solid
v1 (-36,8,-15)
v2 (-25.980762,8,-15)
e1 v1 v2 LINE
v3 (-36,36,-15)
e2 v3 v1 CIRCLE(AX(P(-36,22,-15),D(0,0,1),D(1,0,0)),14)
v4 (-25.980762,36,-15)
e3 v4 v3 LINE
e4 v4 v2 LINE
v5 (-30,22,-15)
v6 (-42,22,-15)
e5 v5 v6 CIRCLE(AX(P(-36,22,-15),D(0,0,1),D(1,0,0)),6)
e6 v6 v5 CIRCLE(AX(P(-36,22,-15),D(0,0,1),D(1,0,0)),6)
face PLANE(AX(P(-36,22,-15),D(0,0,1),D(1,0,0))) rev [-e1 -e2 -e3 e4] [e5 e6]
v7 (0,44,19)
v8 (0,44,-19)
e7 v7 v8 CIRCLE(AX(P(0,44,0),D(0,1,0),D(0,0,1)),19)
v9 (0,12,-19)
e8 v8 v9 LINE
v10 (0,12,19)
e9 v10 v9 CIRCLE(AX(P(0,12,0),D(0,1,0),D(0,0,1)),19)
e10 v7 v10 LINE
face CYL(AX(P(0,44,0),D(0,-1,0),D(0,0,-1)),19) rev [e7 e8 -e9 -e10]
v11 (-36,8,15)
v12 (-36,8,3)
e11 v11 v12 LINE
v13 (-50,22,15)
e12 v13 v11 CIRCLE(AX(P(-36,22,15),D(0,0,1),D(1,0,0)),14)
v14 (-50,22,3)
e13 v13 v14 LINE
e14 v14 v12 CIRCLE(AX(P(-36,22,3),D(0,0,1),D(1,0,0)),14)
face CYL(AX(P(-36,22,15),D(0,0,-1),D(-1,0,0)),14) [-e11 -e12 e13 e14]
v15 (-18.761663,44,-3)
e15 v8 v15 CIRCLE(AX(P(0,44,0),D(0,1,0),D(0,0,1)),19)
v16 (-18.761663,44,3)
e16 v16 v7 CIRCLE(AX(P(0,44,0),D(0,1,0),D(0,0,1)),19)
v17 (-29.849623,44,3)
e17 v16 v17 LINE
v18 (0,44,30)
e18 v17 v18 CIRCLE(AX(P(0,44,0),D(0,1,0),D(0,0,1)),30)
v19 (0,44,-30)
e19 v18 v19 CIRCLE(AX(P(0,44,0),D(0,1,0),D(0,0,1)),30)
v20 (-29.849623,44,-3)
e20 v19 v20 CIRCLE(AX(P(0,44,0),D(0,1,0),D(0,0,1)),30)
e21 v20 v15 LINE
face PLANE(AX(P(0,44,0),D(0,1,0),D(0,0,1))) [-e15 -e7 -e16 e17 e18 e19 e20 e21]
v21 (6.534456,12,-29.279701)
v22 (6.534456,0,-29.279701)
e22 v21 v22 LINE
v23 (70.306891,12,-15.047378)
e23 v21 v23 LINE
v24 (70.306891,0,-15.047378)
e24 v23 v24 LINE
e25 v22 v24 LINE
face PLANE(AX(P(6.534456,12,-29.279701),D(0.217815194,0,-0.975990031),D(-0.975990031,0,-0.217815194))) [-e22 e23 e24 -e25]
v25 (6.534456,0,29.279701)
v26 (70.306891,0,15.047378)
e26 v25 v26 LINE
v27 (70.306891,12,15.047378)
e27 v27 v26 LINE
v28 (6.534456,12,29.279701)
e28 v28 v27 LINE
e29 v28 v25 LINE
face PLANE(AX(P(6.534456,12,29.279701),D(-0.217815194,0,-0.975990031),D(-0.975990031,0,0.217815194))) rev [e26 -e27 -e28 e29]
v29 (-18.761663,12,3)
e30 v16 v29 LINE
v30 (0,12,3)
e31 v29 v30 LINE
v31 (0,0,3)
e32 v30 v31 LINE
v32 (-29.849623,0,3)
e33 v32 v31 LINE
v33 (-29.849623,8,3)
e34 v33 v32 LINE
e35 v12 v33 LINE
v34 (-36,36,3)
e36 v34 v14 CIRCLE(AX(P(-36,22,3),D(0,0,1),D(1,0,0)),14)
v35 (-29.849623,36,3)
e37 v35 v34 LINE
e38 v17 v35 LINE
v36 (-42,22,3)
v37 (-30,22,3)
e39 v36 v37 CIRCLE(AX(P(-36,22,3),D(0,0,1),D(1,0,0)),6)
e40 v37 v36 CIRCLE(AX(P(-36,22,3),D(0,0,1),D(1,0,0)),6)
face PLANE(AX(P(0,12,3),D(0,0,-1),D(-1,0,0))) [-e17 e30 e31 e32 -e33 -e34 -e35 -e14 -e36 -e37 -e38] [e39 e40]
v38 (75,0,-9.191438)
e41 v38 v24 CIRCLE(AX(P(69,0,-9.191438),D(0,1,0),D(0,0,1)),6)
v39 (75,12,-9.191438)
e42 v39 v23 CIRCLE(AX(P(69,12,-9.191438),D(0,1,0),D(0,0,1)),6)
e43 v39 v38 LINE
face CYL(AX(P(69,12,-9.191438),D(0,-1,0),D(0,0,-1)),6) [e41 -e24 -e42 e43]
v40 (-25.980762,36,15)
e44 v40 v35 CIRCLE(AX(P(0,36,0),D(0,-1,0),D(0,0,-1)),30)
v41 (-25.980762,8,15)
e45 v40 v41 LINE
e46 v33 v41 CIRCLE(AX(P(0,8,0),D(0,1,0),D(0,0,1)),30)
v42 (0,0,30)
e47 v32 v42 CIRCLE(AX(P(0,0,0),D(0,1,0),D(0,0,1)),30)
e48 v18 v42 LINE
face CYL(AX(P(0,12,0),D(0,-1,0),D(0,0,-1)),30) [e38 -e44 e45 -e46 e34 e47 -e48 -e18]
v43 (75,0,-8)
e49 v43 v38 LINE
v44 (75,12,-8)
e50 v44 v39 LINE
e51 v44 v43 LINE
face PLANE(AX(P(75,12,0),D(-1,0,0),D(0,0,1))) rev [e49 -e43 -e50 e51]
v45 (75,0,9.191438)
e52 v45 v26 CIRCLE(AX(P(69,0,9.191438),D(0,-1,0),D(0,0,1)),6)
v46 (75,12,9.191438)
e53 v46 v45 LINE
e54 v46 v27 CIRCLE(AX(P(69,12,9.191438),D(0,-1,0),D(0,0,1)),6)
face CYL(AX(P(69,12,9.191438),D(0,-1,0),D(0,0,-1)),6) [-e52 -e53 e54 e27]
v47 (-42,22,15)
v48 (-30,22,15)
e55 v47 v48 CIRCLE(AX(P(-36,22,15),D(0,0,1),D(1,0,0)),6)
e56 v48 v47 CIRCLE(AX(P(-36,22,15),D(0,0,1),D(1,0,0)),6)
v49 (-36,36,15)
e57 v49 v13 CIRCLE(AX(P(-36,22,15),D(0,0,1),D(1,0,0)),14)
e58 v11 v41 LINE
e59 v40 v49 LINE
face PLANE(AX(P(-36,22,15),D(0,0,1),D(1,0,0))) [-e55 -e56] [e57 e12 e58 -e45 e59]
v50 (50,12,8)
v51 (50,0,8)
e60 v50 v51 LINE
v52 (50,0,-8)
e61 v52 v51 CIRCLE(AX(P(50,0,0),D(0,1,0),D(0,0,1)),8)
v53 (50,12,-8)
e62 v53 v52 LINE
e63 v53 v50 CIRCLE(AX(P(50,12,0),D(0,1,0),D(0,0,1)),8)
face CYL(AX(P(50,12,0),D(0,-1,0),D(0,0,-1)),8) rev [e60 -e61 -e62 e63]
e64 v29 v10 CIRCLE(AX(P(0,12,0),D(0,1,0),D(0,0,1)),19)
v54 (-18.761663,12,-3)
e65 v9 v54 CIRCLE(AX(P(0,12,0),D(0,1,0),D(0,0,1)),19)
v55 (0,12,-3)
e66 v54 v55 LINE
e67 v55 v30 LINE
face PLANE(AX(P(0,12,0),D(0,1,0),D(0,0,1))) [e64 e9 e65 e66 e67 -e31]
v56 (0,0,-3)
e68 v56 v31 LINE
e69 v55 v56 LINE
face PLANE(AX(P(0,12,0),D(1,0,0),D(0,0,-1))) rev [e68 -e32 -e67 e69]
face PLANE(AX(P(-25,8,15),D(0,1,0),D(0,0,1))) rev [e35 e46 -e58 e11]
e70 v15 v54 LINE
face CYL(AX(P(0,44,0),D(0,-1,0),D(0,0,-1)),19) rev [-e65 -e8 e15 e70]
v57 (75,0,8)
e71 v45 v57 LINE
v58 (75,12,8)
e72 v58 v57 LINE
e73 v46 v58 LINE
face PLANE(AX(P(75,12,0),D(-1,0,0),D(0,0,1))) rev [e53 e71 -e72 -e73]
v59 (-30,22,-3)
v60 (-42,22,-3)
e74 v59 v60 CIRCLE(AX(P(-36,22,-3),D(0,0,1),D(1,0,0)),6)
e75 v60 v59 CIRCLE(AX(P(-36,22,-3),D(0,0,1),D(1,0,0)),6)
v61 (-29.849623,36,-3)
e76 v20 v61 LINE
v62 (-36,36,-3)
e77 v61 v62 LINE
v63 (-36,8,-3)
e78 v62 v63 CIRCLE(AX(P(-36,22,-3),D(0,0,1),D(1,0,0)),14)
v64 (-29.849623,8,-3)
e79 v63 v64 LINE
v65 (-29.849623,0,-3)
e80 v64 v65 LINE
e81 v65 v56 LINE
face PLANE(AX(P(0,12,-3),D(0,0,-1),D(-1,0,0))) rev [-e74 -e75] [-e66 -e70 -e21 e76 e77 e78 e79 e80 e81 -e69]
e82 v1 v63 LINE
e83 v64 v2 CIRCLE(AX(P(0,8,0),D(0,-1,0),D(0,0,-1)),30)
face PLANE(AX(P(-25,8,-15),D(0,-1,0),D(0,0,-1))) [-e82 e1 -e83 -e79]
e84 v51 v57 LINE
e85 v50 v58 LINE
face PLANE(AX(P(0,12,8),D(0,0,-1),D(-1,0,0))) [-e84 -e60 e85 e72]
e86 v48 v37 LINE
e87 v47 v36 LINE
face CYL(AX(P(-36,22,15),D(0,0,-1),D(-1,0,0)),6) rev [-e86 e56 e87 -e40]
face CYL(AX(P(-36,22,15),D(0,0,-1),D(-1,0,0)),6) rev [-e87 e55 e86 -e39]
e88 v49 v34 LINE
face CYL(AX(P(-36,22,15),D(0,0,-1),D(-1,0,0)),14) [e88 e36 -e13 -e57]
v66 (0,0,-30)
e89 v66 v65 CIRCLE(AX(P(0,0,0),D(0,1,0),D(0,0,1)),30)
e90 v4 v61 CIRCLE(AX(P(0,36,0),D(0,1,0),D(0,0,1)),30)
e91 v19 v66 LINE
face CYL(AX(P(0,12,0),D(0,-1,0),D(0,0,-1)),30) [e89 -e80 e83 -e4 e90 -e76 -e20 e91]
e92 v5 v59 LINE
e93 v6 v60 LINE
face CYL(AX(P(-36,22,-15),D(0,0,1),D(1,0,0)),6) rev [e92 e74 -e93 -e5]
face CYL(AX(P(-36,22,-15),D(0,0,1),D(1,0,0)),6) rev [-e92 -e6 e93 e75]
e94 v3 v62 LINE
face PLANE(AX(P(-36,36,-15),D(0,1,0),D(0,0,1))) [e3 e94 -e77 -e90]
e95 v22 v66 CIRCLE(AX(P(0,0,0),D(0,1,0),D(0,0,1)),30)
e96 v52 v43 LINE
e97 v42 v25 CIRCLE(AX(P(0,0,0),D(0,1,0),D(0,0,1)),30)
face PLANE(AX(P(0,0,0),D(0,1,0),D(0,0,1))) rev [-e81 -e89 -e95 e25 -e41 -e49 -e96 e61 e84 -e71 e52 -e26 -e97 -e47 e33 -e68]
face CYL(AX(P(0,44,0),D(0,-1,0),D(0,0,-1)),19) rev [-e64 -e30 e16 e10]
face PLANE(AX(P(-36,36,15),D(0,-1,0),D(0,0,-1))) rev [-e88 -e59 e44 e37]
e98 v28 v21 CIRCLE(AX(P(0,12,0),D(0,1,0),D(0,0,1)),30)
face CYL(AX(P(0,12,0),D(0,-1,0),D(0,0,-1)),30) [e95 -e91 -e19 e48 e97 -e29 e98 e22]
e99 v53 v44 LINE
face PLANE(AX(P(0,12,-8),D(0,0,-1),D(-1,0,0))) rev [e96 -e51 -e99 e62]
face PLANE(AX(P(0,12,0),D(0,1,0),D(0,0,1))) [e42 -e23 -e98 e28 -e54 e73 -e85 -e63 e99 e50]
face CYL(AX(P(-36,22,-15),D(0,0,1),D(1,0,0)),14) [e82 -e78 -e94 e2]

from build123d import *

# Parameters (mm, degrees)
BASE_FLANGE_DEPTH      = 12
SPLIT_CLAMP_RING_DEPTH = 32
CLAMP_EAR_A_SKETCH_R   = 6
CLAMP_EAR_A_DEPTH      = 12
CLAMP_START            = -12
CLAMP_EAR_B_SKETCH_R   = 6
CLAMP_EAR_B_DEPTH      = 12


with BuildPart() as part:
    # Base Flange Sketch → Base Flange (new body)
    with BuildSketch(Plane(origin=(0, 0, 0), x_dir=(1, 0, 0), z_dir=(0, 1, 0))):
        with BuildLine():
            Line((-29.849623113, 3), (0, 3))
            Line((0, 3), (0, -3))
            Line((0, -3), (-29.849623113, -3))
            ThreePointArc((-29.849623113, -3), (-17.565731604, -24.319643772), (6.534455825, -29.279700939))
            Line((6.534455825, -29.279700939), (70.306891165, -15.047377923))
            ThreePointArc((70.306891165, -15.047377923), (73.681951889, -12.943680599), (75, -9.191437735))
            Line((75, -9.191437735), (75, -8))
            Line((75, -8), (50, -8))
            ThreePointArc((50, -8), (42, 0), (50, 8))
            Line((50, 8), (75, 8))
            Line((75, 8), (75, 9.191437735))
            ThreePointArc((75, 9.191437735), (73.681951889, 12.943680599), (70.306891165, 15.047377923))
            Line((70.306891165, 15.047377923), (6.534455825, 29.279700939))
            ThreePointArc((6.534455825, 29.279700939), (-17.565731604, 24.319643772), (-29.849623113, 3))
        make_face()
    extrude(amount=BASE_FLANGE_DEPTH)

    # Clamp Ring Sketch → Split Clamp Ring (add)
    with BuildSketch(Plane(origin=(0, 12, 0), x_dir=(1, 0, 0), z_dir=(0, 1, 0))):
        with BuildLine():
            ThreePointArc((6.534455825, 29.279700939), (-17.565731604, 24.319643772), (-29.849623113, 3))
            Line((-29.849623113, 3), (-18.761663039, 3))
            ThreePointArc((-18.761663039, 3), (19, 0), (-18.761663039, -3))
            Line((-18.761663039, -3), (-29.849623113, -3))
            ThreePointArc((-29.849623113, -3), (-17.565731604, -24.319643772), (6.534455825, -29.279700939))
            ThreePointArc((6.534455825, -29.279700939), (30, 0), (6.534455825, 29.279700939))
        make_face()
    extrude(amount=SPLIT_CLAMP_RING_DEPTH)

    # Clamp Ear A Sketch → Clamp Ear A (add)
    with BuildSketch(Plane.XY.offset(3)):
        with BuildLine():
            Line((-36, 36), (-25, 36))
            Line((-25, 36), (-25, 8))
            Line((-25, 8), (-36, 8))
            ThreePointArc((-36, 8), (-50, 22), (-36, 36))
        make_face()
        with Locations((-36, 22)):
            Circle(CLAMP_EAR_A_SKETCH_R, mode=Mode.SUBTRACT)
    extrude(amount=CLAMP_EAR_A_DEPTH)

    # Clamp Ear B Sketch → Clamp Ear B (add)
    with BuildSketch(Plane.XY.offset(-3).offset(CLAMP_START)):
        with BuildLine():
            Line((-36, 36), (-25, 36))
            Line((-25, 36), (-25, 8))
            Line((-25, 8), (-36, 8))
            ThreePointArc((-36, 8), (-50, 22), (-36, 36))
        make_face()
        with Locations((-36, 22)):
            Circle(CLAMP_EAR_B_SKETCH_R, mode=Mode.SUBTRACT)
    extrude(amount=CLAMP_EAR_B_DEPTH)


solid = part.part
